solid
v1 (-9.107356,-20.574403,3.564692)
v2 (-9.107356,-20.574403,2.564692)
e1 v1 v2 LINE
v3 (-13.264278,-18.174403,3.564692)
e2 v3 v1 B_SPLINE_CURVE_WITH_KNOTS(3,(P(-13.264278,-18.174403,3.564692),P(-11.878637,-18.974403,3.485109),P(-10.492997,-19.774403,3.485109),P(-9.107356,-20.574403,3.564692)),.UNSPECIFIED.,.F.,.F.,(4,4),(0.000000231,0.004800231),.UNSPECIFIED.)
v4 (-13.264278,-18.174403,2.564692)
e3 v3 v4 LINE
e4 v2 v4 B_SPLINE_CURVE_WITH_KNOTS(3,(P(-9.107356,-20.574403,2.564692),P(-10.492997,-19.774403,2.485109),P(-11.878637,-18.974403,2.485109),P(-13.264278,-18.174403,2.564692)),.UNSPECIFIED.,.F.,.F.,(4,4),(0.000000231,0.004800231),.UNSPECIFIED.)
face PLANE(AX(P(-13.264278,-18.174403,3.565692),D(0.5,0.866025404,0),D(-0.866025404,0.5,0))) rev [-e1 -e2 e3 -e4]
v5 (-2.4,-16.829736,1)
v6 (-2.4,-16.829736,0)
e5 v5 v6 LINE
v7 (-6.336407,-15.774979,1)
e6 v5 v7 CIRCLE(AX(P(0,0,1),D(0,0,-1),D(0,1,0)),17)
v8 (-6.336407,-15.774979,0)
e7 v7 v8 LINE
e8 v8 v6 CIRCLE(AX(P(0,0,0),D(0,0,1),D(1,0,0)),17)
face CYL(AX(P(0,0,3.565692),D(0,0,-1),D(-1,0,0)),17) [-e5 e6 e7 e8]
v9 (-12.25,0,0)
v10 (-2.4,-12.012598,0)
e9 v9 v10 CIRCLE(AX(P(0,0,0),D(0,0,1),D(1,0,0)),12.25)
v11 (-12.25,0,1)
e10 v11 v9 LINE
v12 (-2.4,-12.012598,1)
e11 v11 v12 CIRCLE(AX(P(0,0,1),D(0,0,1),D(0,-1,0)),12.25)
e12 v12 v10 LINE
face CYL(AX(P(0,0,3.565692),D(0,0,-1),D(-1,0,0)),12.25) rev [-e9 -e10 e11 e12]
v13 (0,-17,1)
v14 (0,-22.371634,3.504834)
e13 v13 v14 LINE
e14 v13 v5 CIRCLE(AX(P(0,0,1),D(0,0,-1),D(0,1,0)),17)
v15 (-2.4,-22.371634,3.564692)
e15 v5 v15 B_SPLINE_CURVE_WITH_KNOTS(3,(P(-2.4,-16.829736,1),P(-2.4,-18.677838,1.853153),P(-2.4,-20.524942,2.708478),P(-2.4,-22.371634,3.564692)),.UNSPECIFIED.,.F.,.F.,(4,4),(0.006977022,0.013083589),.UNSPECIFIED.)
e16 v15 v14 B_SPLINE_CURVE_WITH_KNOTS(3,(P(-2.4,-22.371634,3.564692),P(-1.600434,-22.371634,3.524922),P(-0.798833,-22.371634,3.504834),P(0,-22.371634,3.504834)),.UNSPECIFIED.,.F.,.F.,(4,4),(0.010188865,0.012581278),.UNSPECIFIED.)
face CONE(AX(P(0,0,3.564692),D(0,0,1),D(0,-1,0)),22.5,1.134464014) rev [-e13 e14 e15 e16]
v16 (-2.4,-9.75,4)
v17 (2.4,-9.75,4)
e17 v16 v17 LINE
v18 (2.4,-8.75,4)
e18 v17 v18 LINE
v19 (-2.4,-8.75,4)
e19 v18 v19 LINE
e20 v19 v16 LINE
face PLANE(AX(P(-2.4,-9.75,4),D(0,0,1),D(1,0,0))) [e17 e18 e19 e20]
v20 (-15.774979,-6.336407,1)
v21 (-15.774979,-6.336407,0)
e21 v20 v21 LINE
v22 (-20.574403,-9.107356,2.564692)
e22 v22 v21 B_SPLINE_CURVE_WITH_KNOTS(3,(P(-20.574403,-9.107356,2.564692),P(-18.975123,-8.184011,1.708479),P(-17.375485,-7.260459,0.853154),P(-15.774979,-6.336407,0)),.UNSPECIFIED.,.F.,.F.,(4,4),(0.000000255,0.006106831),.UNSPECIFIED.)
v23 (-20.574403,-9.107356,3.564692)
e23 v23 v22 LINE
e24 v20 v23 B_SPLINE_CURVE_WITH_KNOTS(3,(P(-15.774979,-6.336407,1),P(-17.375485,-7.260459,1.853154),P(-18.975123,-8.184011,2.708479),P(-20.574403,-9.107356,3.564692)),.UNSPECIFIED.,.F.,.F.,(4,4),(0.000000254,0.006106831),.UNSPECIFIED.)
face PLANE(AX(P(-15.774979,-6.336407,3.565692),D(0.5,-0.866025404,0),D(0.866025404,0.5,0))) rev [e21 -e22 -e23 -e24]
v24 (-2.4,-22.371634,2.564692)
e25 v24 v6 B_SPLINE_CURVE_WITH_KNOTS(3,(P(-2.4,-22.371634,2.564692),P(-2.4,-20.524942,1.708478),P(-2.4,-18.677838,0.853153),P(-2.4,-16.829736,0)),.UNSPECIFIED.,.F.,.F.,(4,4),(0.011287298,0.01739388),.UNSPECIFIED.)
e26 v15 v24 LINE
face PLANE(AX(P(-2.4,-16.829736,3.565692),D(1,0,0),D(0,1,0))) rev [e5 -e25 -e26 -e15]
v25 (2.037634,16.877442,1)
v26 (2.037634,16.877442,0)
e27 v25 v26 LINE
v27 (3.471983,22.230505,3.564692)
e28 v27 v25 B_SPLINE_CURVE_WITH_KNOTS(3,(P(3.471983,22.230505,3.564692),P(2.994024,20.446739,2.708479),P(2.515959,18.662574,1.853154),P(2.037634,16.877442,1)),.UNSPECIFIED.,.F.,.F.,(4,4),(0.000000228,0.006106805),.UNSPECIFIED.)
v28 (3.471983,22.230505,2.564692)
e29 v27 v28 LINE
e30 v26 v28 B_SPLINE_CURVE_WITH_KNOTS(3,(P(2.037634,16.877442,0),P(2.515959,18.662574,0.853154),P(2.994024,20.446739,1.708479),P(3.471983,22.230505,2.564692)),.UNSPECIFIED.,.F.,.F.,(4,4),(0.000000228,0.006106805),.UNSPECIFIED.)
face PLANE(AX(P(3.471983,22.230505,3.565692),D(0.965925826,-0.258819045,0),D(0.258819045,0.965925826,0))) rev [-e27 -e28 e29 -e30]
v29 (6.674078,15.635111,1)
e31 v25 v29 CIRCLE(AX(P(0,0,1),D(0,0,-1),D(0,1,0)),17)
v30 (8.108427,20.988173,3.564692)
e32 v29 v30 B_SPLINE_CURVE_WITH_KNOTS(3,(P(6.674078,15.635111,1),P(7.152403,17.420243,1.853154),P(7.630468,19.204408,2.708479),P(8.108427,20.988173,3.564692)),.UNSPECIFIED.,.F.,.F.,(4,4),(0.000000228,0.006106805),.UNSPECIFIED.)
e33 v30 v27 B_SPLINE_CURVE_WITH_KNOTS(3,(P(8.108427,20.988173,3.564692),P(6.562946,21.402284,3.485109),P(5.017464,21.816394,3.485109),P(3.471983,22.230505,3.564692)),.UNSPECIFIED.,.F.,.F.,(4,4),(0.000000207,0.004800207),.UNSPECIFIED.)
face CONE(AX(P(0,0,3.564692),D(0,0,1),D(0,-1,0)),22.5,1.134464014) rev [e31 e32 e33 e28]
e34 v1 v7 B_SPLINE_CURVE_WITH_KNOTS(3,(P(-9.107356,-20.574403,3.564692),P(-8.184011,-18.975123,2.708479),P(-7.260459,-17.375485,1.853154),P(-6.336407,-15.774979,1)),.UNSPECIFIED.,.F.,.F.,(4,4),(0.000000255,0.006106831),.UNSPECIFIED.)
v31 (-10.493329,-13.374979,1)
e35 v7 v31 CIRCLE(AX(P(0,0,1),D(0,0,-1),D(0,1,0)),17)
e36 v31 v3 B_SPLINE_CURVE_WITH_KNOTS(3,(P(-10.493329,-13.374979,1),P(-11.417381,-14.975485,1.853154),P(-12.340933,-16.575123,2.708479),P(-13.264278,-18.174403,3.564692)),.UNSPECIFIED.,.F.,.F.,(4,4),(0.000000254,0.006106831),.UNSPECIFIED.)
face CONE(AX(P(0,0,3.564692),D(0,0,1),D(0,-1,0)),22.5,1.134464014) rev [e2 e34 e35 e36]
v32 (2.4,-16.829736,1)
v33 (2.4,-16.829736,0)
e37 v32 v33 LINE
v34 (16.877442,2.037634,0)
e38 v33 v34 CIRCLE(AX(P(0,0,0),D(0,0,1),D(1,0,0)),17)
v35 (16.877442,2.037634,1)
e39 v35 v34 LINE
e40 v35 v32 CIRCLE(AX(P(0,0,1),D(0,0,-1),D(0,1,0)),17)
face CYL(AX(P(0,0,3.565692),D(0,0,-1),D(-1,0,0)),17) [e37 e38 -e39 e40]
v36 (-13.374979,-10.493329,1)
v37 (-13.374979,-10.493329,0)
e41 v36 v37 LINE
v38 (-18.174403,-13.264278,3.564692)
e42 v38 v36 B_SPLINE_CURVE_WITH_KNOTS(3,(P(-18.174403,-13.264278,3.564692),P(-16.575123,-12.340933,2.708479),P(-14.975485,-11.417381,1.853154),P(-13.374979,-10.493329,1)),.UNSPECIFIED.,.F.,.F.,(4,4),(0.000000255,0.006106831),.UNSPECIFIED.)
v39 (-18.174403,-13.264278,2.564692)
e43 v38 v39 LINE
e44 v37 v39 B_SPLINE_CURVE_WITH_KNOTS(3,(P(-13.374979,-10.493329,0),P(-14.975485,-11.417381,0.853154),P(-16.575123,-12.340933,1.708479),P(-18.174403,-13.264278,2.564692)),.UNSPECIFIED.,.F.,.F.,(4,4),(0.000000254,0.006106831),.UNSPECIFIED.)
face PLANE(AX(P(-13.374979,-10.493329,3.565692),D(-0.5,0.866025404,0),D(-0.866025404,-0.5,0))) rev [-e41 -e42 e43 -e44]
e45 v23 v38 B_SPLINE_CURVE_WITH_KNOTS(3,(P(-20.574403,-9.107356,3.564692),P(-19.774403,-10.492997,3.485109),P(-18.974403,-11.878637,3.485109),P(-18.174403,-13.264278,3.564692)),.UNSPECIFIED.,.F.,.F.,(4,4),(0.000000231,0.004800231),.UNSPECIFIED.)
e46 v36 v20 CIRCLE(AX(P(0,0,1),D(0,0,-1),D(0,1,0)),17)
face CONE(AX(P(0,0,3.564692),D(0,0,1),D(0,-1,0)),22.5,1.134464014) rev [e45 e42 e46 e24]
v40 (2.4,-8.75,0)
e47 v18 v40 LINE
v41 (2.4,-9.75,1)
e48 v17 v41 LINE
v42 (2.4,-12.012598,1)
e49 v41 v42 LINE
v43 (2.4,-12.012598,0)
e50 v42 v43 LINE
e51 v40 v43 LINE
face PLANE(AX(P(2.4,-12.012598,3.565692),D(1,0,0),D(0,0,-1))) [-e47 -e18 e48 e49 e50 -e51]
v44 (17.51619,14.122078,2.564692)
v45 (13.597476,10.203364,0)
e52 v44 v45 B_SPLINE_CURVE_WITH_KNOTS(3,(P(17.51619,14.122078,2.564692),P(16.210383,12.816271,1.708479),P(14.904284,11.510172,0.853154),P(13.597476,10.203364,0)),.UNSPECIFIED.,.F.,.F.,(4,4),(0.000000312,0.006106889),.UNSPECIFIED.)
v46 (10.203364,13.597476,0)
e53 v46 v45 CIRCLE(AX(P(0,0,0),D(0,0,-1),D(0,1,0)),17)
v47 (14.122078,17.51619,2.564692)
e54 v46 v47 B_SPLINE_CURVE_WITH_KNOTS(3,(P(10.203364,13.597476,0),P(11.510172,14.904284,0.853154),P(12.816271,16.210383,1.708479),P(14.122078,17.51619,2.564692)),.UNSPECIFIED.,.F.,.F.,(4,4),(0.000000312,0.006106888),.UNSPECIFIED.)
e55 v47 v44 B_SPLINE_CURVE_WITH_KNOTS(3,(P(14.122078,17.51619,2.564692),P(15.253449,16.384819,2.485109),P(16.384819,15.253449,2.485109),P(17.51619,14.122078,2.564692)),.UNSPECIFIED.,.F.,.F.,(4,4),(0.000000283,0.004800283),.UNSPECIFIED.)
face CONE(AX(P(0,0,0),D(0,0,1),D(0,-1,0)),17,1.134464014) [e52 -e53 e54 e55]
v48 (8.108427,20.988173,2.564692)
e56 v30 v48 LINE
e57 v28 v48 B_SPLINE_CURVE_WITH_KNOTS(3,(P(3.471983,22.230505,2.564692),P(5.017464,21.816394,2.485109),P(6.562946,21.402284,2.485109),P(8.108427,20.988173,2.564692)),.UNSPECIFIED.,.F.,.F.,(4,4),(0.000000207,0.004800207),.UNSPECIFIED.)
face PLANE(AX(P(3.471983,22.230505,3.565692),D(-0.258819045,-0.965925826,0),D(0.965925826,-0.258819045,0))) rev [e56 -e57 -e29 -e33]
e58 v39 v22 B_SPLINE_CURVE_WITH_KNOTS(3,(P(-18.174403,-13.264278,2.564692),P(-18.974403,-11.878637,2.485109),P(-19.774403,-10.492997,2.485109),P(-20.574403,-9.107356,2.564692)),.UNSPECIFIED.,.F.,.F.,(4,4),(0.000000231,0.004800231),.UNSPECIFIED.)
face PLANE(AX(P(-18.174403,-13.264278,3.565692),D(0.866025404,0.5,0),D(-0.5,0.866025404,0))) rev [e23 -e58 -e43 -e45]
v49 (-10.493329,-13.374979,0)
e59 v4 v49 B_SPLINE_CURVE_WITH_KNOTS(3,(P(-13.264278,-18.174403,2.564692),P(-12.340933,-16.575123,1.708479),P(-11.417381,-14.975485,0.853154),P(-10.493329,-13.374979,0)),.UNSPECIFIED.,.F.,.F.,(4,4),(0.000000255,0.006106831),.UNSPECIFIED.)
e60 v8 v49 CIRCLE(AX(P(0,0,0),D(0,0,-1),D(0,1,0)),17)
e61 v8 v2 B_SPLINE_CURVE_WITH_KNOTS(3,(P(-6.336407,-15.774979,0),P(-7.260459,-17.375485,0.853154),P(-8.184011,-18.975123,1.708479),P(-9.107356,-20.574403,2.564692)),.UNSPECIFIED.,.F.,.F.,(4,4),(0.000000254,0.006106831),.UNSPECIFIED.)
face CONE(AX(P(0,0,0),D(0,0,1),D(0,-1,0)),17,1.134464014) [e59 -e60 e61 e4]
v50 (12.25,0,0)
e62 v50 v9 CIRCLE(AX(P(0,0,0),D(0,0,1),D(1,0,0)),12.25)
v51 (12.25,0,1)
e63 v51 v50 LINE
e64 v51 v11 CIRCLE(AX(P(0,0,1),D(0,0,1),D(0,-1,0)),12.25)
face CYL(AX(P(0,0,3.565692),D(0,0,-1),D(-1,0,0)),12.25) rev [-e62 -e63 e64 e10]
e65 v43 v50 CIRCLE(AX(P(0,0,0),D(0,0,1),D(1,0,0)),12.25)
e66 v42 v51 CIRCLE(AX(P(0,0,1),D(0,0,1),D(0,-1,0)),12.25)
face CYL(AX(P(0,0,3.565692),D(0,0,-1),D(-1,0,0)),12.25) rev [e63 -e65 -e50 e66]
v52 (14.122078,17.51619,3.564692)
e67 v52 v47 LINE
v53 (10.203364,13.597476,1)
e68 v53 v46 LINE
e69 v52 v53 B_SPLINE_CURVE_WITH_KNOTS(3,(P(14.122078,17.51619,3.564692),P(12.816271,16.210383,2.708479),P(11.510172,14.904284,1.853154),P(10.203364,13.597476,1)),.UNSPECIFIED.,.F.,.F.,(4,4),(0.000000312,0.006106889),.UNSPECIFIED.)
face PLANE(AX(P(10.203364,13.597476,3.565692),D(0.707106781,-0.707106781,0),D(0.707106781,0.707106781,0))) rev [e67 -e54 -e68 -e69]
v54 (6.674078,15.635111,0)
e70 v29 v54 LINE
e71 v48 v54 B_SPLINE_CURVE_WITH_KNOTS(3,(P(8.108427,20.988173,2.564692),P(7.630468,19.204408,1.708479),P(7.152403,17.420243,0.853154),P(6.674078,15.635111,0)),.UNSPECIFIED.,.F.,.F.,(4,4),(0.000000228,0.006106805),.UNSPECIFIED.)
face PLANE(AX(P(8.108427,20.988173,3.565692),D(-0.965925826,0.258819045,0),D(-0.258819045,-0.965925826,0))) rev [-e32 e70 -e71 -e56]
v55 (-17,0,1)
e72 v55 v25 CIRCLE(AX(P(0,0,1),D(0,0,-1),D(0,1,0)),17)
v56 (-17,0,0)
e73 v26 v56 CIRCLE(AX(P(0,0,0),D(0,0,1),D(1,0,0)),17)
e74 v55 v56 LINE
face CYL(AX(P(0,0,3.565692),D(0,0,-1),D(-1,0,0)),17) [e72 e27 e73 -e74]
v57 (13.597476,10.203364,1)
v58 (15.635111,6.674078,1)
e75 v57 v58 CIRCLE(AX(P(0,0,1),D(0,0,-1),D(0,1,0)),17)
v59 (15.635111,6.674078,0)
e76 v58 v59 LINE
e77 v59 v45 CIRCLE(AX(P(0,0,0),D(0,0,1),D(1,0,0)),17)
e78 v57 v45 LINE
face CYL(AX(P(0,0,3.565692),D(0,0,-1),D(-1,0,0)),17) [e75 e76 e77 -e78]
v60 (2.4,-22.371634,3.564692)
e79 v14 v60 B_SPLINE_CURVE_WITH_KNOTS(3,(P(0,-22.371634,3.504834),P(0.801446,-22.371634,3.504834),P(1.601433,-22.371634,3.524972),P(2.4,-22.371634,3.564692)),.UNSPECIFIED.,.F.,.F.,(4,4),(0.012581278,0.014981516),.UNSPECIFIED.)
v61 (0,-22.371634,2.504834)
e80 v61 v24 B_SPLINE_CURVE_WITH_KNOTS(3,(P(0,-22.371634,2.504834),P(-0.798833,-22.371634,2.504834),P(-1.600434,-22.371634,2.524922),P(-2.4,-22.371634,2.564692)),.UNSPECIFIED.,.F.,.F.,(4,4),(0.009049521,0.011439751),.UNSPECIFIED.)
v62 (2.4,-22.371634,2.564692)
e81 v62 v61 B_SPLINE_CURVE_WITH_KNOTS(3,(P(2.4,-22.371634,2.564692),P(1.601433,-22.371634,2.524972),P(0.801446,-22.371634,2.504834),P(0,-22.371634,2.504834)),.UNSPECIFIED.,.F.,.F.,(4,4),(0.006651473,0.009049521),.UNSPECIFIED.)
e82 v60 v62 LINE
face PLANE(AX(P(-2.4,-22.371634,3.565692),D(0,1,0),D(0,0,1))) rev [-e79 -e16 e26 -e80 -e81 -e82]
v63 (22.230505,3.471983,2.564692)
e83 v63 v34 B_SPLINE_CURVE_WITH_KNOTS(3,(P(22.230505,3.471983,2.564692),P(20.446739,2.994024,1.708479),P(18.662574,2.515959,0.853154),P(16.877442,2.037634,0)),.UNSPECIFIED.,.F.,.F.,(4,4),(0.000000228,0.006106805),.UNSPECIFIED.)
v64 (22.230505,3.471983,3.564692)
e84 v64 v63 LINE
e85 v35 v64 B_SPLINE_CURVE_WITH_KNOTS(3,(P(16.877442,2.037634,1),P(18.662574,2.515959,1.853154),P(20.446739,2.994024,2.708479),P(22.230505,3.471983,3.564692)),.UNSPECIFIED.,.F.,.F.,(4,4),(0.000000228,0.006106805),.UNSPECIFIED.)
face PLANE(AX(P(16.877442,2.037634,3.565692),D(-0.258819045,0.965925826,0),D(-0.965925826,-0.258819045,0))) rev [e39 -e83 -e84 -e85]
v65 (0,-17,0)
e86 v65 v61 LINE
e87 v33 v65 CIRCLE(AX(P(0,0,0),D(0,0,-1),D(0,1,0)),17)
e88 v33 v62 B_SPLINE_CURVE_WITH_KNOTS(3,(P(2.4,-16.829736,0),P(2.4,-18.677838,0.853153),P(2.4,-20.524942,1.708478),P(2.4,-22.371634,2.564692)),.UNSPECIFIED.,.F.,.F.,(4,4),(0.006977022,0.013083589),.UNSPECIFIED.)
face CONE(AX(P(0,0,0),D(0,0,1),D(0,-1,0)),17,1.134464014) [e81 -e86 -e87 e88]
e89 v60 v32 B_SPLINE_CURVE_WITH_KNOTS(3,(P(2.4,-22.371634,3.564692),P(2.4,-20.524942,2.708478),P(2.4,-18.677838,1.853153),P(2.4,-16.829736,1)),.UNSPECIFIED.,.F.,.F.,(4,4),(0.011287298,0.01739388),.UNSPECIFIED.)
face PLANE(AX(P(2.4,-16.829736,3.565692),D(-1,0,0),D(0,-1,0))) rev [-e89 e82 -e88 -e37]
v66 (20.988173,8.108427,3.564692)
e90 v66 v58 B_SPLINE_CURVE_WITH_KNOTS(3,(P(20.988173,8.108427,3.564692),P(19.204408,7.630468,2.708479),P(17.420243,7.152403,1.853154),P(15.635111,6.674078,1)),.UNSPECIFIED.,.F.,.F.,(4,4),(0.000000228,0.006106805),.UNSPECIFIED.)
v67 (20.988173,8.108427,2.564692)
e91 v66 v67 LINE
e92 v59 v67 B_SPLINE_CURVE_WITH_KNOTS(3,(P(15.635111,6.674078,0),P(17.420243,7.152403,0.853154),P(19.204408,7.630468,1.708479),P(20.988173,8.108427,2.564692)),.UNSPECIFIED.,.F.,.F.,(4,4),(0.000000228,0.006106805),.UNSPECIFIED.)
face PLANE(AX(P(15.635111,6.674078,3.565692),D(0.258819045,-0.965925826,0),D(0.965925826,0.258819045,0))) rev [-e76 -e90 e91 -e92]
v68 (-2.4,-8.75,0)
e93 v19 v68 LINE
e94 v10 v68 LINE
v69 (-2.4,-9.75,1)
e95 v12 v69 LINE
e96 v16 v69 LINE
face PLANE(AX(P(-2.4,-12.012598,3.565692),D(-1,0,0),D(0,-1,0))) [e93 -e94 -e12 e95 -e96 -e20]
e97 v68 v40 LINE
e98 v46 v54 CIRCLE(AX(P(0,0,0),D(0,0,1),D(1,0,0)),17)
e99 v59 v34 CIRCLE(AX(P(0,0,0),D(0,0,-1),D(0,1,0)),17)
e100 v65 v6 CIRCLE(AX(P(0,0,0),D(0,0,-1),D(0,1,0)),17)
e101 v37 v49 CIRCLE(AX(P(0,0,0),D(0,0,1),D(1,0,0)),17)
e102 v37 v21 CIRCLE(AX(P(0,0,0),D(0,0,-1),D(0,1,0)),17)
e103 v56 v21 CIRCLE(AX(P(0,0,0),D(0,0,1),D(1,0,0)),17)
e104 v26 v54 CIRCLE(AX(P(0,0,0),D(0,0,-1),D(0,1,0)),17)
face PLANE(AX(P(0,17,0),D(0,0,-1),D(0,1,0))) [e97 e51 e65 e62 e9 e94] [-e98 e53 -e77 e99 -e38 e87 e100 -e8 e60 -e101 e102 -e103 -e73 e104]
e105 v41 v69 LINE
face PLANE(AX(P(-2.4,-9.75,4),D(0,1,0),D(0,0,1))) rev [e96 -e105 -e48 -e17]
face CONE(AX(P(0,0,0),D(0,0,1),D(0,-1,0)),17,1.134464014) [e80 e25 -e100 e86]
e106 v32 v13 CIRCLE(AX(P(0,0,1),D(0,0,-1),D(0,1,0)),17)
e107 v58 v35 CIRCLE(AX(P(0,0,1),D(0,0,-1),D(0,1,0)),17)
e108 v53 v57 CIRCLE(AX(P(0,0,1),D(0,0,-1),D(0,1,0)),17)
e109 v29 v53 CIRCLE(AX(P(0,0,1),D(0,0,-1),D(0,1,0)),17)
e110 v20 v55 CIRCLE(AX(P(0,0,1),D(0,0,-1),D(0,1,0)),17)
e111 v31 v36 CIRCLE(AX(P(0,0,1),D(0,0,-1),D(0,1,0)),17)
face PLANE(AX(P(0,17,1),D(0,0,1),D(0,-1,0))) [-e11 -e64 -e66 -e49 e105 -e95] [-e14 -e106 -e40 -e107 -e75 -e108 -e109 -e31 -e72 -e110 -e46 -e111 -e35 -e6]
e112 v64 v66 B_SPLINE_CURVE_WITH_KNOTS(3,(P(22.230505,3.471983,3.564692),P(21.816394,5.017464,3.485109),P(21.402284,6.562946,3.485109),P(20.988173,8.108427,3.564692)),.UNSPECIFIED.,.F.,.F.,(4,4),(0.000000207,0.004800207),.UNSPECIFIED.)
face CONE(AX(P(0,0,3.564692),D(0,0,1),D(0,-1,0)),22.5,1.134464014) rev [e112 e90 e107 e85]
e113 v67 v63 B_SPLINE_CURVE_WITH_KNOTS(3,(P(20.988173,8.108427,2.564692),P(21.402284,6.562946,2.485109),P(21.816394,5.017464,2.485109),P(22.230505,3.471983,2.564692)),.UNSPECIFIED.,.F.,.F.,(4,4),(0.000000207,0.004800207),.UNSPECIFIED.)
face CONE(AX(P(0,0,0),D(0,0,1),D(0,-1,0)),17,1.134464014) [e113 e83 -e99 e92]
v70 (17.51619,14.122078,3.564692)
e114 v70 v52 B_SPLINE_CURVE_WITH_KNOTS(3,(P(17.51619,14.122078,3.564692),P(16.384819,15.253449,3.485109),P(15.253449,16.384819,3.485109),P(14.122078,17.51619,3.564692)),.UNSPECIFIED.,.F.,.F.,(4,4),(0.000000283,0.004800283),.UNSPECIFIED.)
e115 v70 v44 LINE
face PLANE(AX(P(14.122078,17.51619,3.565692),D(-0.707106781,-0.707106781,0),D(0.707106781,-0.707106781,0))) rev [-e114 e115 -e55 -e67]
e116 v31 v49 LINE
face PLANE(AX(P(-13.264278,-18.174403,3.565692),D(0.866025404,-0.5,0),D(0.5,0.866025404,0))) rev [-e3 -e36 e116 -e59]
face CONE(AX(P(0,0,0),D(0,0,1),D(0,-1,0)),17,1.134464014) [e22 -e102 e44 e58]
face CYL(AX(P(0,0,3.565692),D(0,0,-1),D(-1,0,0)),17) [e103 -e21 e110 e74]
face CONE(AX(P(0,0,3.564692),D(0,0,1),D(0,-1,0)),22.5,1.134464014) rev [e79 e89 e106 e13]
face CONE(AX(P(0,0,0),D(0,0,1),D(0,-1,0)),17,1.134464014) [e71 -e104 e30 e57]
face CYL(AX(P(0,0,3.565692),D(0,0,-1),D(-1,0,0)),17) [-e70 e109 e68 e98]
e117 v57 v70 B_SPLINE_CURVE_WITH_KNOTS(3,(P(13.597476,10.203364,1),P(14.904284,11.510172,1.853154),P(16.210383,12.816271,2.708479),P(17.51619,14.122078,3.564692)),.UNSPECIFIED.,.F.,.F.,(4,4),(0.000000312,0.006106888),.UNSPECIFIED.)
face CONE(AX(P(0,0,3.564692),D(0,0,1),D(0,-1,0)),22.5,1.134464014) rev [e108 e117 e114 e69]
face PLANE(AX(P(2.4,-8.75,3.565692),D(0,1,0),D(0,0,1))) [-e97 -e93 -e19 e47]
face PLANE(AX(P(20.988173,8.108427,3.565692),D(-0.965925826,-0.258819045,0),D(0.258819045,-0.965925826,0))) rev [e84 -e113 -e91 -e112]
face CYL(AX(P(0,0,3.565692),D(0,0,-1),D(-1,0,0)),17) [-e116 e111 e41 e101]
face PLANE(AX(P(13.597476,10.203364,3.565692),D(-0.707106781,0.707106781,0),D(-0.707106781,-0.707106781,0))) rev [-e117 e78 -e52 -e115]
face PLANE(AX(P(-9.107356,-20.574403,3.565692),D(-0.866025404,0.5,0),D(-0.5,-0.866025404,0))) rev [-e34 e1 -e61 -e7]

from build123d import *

# Parameters (mm, degrees)
CUT_EXTRUDE2_START  = -3e-06
SKETCH3_OUTSIDE_W   = 59.748
SKETCH3_OUTSIDE_H   = 59.748
CUT_EXTRUDE2_DEPTH  = 3.564697
SKETCH4_W           = 4.8
SKETCH4_H           = 1
BOSS_EXTRUDE1_DEPTH = 4


with BuildPart() as part:
    # Sketch2 → Boss-Revolve1 (revolve)
    with BuildSketch(Plane(origin=(0, 0, 0), x_dir=(0, 0, -1), z_dir=(1, 0, 0))):
        Polygon((-2.56469212, 22.5), (0, 17), (0, 0), (-1, 0), (-1, 17), (-3.56469212, 22.5), align=None)
    revolve(axis=Axis((0, 0, 0), (0, 0, 1)))

    # Sketch3 outside → Cut-Extrude2 (cut)
    # profile 1 of 2: a face of its own
    with BuildSketch(Plane.XY.offset(CUT_EXTRUDE2_START)):
        Rectangle(SKETCH3_OUTSIDE_W, SKETCH3_OUTSIDE_H)
        with BuildLine():
            Line((-2.4, -16.829735589), (-2.4, -22.371633825))
            Line((-2.4, -22.371633825), (2.4, -22.371633825))
            Line((2.4, -22.371633825), (2.4, -16.829735589))
            ThreePointArc((2.4, -16.829735589), (13.487006785, -10.348944293), (16.877441963, 2.037634111))
            Line((16.877441963, 2.037634111), (22.230504596, 3.471982921))
            Line((22.230504596, 3.471982921), (20.98817318, 8.108426887))
            Line((20.98817318, 8.108426887), (15.635110547, 6.674078078))
            ThreePointArc((15.635110547, 6.674078078), (14.722431864, 8.5), (13.597476435, 10.203363886))
            Line((13.597476435, 10.203363886), (17.516190259, 14.122077709))
            Line((17.516190259, 14.122077709), (14.122077709, 17.516190259))
            Line((14.122077709, 17.516190259), (10.203363886, 13.597476435))
            ThreePointArc((10.203363886, 13.597476435), (8.5, 14.722431864), (6.674078078, 15.635110547))
            Line((6.674078078, 15.635110547), (8.108426887, 20.98817318))
            Line((8.108426887, 20.98817318), (3.471982921, 22.230504596))
            Line((3.471982921, 22.230504596), (2.037634111, 16.877441963))
            ThreePointArc((2.037634111, 16.877441963), (-13.487006785, 10.348944293), (-15.774978559, -6.336406825))
            Line((-15.774978559, -6.336406825), (-20.574403217, -9.107355943))
            Line((-20.574403217, -9.107355943), (-18.174403217, -13.264277882))
            Line((-18.174403217, -13.264277882), (-13.374978559, -10.493328764))
            ThreePointArc((-13.374978559, -10.493328764), (-12.02081528, -12.02081528), (-10.493328764, -13.374978559))
            Line((-10.493328764, -13.374978559), (-13.264277882, -18.174403217))
            Line((-13.264277882, -18.174403217), (-9.107355943, -20.574403217))
            Line((-9.107355943, -20.574403217), (-6.336406825, -15.774978559))
            ThreePointArc((-6.336406825, -15.774978559), (-4.399923767, -16.420739047), (-2.4, -16.829735589))
        make_face(mode=Mode.SUBTRACT)
    # profile 2 of 2: a face of its own
    with BuildSketch(Plane.XY.offset(CUT_EXTRUDE2_START)):
        with BuildLine():
            Line((2.4, -12.012597554), (2.4, -8.75))
            Line((2.4, -8.75), (-2.4, -8.75))
            Line((-2.4, -8.75), (-2.4, -12.012597554))
            ThreePointArc((-2.4, -12.012597554), (0, 12.25), (2.4, -12.012597554))
        make_face()
    extrude(amount=CUT_EXTRUDE2_DEPTH, mode=Mode.SUBTRACT)

    # Sketch4 → Boss-Extrude1 (add)
    with BuildSketch(Plane.XY):
        with Locations((0, -9.25)):
            Rectangle(SKETCH4_W, SKETCH4_H)
    extrude(amount=BOSS_EXTRUDE1_DEPTH)


solid = part.part
